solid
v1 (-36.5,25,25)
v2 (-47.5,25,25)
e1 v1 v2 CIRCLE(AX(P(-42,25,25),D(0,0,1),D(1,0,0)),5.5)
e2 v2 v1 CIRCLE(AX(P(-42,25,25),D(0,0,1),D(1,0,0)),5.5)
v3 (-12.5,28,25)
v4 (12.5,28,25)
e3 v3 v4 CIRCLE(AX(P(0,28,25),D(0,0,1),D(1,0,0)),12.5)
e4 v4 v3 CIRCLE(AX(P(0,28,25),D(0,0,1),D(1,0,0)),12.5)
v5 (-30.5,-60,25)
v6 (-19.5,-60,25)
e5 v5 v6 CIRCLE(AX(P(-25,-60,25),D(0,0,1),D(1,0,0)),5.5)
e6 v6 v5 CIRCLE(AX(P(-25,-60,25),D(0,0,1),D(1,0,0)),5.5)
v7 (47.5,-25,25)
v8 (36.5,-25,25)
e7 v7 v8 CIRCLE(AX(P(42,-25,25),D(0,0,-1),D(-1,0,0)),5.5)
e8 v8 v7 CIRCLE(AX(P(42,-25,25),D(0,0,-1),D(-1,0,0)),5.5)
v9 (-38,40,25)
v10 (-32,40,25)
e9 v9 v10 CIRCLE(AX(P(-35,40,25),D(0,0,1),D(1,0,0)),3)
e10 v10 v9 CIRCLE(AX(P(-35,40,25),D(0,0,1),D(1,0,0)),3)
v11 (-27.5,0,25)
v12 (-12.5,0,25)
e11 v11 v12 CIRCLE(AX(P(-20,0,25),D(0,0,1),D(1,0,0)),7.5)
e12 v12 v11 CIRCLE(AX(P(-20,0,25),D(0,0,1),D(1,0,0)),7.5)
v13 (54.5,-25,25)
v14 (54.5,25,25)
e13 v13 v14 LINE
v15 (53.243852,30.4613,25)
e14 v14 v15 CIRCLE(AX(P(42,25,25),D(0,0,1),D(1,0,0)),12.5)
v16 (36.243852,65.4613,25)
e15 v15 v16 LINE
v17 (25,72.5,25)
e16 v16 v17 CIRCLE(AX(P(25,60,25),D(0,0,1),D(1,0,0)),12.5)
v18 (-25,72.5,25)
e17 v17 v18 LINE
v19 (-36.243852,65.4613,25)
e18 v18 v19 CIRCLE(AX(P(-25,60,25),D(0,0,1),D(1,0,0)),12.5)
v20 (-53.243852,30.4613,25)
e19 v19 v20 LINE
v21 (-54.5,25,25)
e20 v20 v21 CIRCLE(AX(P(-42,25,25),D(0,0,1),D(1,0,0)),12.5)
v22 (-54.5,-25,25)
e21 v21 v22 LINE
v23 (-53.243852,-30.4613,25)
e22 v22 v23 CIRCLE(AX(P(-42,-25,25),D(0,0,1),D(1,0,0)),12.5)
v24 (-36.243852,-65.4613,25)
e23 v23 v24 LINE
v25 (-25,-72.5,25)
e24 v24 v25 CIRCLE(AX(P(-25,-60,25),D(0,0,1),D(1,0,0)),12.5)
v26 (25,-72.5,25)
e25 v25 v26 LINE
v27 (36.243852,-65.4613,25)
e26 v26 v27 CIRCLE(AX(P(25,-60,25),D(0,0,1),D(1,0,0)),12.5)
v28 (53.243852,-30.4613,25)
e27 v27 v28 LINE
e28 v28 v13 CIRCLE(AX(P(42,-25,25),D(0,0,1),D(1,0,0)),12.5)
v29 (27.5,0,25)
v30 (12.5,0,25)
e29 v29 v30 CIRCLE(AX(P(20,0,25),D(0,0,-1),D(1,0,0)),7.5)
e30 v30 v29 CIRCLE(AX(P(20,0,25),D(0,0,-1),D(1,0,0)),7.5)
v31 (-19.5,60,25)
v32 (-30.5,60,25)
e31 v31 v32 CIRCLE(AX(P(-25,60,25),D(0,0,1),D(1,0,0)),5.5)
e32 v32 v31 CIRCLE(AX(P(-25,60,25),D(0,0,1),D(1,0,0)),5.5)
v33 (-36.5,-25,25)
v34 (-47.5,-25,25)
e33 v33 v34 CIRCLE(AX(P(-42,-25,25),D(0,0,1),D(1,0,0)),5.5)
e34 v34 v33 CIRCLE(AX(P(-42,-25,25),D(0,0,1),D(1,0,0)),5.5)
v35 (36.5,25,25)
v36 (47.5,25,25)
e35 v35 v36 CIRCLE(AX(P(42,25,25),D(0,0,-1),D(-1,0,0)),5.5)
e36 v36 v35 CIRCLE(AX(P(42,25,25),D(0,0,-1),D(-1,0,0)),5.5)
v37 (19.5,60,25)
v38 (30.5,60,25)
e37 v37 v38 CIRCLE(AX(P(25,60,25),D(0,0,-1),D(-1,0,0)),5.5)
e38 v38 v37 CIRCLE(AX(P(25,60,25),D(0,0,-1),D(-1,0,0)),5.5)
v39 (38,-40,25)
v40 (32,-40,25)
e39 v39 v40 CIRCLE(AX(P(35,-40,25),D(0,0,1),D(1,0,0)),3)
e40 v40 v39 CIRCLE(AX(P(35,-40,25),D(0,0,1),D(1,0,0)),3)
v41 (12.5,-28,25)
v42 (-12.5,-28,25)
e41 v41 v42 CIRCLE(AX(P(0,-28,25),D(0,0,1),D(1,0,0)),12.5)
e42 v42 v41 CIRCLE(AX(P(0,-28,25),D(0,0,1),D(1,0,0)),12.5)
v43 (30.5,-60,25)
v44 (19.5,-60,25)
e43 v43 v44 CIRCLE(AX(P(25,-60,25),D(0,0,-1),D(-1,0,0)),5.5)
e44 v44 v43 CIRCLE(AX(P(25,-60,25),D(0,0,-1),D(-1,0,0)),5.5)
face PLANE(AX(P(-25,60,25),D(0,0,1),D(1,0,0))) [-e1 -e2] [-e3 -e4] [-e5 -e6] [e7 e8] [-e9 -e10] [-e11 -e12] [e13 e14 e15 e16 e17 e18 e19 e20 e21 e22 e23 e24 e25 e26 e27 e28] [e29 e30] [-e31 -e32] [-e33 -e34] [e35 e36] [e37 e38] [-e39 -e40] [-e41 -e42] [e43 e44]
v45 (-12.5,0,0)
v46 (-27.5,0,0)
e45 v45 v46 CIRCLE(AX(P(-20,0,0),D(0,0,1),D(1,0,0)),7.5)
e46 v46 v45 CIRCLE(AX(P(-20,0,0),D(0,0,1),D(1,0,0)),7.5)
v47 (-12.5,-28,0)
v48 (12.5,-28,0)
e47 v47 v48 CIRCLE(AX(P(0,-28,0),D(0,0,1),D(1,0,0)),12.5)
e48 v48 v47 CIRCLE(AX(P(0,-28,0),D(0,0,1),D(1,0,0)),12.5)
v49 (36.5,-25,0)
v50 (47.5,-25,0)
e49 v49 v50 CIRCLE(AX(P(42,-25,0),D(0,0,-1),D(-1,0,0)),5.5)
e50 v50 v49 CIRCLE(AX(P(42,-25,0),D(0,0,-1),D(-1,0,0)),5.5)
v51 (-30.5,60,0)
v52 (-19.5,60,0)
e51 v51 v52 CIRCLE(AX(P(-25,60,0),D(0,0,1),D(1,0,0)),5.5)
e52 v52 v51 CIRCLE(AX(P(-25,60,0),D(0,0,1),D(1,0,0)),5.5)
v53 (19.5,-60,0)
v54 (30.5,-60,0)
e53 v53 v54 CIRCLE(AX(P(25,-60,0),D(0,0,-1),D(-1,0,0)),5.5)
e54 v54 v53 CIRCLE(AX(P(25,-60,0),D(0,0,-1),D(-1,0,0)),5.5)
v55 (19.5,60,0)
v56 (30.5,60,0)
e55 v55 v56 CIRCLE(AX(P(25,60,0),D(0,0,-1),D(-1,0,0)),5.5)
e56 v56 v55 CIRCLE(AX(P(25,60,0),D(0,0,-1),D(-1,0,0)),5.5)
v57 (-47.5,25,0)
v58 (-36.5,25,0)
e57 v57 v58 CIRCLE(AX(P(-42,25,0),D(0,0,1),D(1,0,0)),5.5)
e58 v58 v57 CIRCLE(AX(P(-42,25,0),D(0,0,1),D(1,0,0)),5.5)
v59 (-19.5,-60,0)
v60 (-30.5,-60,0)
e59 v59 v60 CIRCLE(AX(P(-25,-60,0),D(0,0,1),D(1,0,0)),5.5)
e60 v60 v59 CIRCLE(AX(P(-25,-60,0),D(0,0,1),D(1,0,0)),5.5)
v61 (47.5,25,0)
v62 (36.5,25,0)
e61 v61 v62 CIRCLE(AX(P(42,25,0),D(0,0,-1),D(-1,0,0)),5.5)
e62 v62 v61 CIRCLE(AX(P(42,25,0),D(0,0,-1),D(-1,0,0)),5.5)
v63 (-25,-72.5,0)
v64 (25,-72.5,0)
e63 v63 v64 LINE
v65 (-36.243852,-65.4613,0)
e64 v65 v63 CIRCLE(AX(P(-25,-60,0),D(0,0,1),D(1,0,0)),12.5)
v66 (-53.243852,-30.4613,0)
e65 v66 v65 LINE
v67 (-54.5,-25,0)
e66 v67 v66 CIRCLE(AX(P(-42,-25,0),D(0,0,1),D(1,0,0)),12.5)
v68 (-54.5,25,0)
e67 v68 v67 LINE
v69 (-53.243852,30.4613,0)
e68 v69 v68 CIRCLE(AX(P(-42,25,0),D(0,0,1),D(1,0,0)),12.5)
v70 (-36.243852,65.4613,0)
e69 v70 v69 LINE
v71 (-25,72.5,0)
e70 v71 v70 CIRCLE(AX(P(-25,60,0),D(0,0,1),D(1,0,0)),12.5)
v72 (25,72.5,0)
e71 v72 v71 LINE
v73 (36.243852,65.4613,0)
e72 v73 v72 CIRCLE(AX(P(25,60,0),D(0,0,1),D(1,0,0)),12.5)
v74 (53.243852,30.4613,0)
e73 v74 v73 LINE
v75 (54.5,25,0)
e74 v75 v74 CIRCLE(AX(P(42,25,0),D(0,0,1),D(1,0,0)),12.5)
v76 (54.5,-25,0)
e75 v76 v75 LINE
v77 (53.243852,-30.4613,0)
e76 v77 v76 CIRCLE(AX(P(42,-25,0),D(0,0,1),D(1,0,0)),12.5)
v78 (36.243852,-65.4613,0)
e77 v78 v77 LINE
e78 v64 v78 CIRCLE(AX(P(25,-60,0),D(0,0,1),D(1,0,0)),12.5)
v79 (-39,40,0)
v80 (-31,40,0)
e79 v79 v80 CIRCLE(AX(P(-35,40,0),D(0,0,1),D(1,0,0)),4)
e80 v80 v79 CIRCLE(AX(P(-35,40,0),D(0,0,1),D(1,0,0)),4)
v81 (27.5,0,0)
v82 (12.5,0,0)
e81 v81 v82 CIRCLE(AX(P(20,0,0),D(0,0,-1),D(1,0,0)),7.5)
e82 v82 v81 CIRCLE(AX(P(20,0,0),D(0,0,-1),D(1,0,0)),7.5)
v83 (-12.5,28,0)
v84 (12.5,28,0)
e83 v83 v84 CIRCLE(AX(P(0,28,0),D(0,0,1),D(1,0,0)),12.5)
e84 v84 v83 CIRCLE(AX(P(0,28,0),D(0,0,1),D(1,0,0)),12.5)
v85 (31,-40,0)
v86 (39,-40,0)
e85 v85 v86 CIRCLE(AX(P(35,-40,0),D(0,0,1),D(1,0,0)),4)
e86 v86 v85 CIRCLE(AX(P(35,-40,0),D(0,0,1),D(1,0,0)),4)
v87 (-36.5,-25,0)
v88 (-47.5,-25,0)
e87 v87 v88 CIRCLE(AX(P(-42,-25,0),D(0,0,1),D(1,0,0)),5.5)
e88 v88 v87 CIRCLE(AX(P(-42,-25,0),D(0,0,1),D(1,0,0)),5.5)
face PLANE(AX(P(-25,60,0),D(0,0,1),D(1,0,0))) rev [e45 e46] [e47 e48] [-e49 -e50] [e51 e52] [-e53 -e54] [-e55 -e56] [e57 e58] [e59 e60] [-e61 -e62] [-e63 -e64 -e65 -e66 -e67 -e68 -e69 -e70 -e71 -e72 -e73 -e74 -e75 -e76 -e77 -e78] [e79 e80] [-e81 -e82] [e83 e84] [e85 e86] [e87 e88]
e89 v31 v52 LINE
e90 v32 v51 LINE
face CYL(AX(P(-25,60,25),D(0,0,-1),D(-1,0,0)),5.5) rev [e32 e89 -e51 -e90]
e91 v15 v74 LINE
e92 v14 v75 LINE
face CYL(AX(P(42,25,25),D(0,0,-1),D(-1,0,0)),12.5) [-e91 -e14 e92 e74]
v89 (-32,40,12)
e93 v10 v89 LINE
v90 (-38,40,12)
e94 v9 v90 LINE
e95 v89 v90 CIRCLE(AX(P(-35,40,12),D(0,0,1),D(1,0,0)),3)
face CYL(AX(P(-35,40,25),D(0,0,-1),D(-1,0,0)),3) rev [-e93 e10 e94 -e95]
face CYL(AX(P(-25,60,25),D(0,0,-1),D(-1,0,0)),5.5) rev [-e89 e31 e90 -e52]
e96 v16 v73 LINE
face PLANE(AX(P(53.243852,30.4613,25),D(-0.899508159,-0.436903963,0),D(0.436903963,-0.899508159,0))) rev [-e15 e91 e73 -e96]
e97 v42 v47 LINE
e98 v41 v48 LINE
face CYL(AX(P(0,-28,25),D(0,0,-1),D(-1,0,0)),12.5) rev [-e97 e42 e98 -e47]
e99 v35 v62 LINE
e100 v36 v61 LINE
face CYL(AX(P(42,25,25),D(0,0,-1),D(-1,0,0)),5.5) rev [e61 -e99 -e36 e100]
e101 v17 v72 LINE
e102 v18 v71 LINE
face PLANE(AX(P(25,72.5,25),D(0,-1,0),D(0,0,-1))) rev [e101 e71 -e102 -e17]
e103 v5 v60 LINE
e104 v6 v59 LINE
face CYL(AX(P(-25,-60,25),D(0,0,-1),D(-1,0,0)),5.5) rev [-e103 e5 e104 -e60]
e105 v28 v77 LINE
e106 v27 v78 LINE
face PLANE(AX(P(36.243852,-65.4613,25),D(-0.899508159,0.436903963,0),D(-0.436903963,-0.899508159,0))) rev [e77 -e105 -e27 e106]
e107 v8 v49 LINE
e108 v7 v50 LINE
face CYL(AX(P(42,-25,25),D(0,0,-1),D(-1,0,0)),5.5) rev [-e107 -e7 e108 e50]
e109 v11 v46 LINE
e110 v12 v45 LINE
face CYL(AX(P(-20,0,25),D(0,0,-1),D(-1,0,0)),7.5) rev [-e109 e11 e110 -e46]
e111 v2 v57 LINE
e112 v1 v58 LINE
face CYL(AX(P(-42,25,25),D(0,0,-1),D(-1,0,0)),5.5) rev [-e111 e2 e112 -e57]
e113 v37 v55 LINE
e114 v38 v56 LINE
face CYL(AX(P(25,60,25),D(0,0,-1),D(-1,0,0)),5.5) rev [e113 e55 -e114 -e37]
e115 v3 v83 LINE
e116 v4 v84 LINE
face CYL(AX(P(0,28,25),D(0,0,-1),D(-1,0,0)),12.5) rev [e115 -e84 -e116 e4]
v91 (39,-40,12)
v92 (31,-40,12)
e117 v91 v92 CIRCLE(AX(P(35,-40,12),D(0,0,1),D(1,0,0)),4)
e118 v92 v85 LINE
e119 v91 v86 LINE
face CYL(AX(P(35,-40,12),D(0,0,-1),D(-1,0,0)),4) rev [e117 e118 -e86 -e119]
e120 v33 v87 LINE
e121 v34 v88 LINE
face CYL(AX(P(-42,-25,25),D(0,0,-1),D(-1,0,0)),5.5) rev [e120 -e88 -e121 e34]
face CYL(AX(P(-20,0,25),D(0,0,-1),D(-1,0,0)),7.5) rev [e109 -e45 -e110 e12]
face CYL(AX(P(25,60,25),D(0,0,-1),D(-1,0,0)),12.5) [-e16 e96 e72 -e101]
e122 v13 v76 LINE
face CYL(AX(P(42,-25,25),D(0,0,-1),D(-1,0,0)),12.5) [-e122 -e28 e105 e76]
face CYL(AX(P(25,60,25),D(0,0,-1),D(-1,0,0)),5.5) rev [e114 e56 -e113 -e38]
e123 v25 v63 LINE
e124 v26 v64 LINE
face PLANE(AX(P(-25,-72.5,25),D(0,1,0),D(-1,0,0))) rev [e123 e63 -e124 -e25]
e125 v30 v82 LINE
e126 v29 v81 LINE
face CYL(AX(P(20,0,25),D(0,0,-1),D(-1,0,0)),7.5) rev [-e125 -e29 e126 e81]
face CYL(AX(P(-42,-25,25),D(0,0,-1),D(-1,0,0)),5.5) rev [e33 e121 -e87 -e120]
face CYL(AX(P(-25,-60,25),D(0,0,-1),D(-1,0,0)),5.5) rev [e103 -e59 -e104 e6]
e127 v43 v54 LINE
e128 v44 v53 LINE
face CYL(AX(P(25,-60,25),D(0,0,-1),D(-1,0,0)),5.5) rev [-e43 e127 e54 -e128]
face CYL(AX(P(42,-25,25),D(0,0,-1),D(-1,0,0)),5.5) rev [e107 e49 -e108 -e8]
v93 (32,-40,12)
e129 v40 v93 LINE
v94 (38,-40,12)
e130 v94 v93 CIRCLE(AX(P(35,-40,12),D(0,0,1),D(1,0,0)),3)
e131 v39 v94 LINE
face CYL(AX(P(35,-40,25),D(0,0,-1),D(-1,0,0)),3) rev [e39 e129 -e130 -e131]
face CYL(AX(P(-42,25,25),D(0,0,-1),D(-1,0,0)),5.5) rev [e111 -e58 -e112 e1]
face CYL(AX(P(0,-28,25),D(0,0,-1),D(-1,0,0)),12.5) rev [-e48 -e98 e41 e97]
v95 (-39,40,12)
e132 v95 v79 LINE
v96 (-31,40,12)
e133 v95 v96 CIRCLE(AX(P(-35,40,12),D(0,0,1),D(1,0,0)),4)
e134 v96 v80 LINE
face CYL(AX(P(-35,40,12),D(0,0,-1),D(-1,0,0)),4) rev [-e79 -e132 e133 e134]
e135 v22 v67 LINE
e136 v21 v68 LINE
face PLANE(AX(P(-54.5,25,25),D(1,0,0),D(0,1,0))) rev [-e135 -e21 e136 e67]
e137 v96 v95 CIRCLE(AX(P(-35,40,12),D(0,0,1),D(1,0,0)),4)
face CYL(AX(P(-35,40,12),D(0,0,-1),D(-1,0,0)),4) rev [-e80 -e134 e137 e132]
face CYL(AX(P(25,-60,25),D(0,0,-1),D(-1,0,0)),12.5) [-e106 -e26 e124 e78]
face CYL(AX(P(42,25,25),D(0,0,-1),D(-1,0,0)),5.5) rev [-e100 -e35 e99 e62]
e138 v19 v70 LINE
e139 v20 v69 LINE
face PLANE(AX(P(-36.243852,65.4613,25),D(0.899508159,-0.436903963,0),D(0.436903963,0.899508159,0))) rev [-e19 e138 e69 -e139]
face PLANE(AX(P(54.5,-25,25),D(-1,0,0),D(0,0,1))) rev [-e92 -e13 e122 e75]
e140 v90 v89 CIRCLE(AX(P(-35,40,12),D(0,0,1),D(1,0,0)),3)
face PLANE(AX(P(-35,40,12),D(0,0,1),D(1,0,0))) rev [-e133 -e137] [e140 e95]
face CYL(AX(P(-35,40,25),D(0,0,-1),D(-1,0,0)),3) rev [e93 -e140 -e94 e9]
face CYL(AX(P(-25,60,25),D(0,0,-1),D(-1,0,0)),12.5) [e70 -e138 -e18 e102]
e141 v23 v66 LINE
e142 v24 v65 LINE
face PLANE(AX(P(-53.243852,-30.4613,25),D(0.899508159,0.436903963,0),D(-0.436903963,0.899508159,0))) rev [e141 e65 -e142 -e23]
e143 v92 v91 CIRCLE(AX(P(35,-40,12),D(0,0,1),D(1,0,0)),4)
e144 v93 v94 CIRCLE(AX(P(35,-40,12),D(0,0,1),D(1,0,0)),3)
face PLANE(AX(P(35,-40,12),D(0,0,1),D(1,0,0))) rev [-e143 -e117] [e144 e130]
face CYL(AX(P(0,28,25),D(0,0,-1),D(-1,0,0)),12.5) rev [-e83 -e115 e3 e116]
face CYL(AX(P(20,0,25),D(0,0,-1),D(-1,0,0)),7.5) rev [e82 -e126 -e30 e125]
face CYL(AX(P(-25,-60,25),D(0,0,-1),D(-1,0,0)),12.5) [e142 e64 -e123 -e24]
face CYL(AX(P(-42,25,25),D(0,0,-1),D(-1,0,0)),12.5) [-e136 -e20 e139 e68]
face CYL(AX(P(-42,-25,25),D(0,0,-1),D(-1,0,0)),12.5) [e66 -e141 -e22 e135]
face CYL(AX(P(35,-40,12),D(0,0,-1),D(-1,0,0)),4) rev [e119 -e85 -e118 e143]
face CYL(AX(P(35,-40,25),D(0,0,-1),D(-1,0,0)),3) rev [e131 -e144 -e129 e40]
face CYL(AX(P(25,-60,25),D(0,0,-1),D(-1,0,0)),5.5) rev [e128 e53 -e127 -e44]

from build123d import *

# Parameters (mm, degrees)
BOSS_EXTRUDE2_DEPTH = 25
SKETCH_19_5_R       = 5.5
SKETCH_19_5_R_2     = 12.5
SKETCH_19_5_R_3     = 7.5
CUT_EXTRUDE1_DEPTH  = 95.082410683
SKETCH_19_6_R       = 3
CUT_EXTRUDE5_DEPTH  = 95.082410683
SKETCH_19_7_2_R     = 4
CUT_EXTRUDE7_DEPTH  = 12


with BuildPart() as part:
    # Sketch 19_7 → Boss-Extrude2 (new body)
    with BuildSketch(Plane.XY):
        with BuildLine():
            Line((54.5, -25), (54.5, 25))
            ThreePointArc((54.5, 25), (54.181915896, 27.801950234), (53.243851982, 30.461299534))
            Line((53.243851982, 30.461299534), (36.243851982, 65.461299534))
            ThreePointArc((36.243851982, 65.461299534), (31.632637327, 70.595193348), (25, 72.5))
            Line((25, 72.5), (-25, 72.5))
            ThreePointArc((-25, 72.5), (-31.632637327, 70.595193348), (-36.243851982, 65.461299534))
            Line((-36.243851982, 65.461299534), (-53.243851982, 30.461299534))
            ThreePointArc((-53.243851982, 30.461299534), (-54.181915896, 27.801950234), (-54.5, 25))
            Line((-54.5, 25), (-54.5, -25))
            ThreePointArc((-54.5, -25), (-54.181915896, -27.801950234), (-53.243851982, -30.461299534))
            Line((-53.243851982, -30.461299534), (-36.243851982, -65.461299534))
            ThreePointArc((-36.243851982, -65.461299534), (-31.632637327, -70.595193348), (-25, -72.5))
            Line((-25, -72.5), (25, -72.5))
            ThreePointArc((25, -72.5), (31.632637327, -70.595193348), (36.243851982, -65.461299534))
            Line((36.243851982, -65.461299534), (53.243851982, -30.461299534))
            ThreePointArc((53.243851982, -30.461299534), (54.181915896, -27.801950234), (54.5, -25))
        make_face()
    extrude(amount=BOSS_EXTRUDE2_DEPTH)

    # 草图19<5> → Cut-Extrude1 (cut, through all)
    with BuildSketch(Plane.XY):
        with Locations((-25, 60)):
            Circle(SKETCH_19_5_R)
        with Locations((-42, 25)):
            Circle(SKETCH_19_5_R)
        with Locations((-42, -25)):
            Circle(SKETCH_19_5_R)
        with Locations((0, -28)):
            Circle(SKETCH_19_5_R_2)
        with Locations((20, 0)):
            Circle(SKETCH_19_5_R_3)
        with Locations((-20, 0)):
            Circle(SKETCH_19_5_R_3)
        with Locations((0, 28)):
            Circle(SKETCH_19_5_R_2)
        with Locations((-25, -60)):
            Circle(SKETCH_19_5_R)
    cut_extrude1 = extrude(amount=CUT_EXTRUDE1_DEPTH, mode=Mode.SUBTRACT)

    # Mirror1: Cut-Extrude1 across plane
    add(cut_extrude1.mirror(Plane(origin=(0, 0, 0), x_dir=(0, 0, 1), z_dir=(1, 0, 0))), mode=Mode.SUBTRACT)

    # 草图19<6> → Cut-Extrude5 (cut, through all)
    with BuildSketch(Plane.XY):
        with Locations((35, -40)):
            Circle(SKETCH_19_6_R)
        with Locations((-35, 40)):
            Circle(SKETCH_19_6_R)
    extrude(amount=CUT_EXTRUDE5_DEPTH, mode=Mode.SUBTRACT)

    # Sketch 19_7 2 → Cut-Extrude7 (cut)
    with BuildSketch(Plane.XY):
        with Locations((-35, 40)):
            Circle(SKETCH_19_7_2_R)
        with Locations((35, -40)):
            Circle(SKETCH_19_7_2_R)
    extrude(amount=CUT_EXTRUDE7_DEPTH, mode=Mode.SUBTRACT)


solid = part.part
